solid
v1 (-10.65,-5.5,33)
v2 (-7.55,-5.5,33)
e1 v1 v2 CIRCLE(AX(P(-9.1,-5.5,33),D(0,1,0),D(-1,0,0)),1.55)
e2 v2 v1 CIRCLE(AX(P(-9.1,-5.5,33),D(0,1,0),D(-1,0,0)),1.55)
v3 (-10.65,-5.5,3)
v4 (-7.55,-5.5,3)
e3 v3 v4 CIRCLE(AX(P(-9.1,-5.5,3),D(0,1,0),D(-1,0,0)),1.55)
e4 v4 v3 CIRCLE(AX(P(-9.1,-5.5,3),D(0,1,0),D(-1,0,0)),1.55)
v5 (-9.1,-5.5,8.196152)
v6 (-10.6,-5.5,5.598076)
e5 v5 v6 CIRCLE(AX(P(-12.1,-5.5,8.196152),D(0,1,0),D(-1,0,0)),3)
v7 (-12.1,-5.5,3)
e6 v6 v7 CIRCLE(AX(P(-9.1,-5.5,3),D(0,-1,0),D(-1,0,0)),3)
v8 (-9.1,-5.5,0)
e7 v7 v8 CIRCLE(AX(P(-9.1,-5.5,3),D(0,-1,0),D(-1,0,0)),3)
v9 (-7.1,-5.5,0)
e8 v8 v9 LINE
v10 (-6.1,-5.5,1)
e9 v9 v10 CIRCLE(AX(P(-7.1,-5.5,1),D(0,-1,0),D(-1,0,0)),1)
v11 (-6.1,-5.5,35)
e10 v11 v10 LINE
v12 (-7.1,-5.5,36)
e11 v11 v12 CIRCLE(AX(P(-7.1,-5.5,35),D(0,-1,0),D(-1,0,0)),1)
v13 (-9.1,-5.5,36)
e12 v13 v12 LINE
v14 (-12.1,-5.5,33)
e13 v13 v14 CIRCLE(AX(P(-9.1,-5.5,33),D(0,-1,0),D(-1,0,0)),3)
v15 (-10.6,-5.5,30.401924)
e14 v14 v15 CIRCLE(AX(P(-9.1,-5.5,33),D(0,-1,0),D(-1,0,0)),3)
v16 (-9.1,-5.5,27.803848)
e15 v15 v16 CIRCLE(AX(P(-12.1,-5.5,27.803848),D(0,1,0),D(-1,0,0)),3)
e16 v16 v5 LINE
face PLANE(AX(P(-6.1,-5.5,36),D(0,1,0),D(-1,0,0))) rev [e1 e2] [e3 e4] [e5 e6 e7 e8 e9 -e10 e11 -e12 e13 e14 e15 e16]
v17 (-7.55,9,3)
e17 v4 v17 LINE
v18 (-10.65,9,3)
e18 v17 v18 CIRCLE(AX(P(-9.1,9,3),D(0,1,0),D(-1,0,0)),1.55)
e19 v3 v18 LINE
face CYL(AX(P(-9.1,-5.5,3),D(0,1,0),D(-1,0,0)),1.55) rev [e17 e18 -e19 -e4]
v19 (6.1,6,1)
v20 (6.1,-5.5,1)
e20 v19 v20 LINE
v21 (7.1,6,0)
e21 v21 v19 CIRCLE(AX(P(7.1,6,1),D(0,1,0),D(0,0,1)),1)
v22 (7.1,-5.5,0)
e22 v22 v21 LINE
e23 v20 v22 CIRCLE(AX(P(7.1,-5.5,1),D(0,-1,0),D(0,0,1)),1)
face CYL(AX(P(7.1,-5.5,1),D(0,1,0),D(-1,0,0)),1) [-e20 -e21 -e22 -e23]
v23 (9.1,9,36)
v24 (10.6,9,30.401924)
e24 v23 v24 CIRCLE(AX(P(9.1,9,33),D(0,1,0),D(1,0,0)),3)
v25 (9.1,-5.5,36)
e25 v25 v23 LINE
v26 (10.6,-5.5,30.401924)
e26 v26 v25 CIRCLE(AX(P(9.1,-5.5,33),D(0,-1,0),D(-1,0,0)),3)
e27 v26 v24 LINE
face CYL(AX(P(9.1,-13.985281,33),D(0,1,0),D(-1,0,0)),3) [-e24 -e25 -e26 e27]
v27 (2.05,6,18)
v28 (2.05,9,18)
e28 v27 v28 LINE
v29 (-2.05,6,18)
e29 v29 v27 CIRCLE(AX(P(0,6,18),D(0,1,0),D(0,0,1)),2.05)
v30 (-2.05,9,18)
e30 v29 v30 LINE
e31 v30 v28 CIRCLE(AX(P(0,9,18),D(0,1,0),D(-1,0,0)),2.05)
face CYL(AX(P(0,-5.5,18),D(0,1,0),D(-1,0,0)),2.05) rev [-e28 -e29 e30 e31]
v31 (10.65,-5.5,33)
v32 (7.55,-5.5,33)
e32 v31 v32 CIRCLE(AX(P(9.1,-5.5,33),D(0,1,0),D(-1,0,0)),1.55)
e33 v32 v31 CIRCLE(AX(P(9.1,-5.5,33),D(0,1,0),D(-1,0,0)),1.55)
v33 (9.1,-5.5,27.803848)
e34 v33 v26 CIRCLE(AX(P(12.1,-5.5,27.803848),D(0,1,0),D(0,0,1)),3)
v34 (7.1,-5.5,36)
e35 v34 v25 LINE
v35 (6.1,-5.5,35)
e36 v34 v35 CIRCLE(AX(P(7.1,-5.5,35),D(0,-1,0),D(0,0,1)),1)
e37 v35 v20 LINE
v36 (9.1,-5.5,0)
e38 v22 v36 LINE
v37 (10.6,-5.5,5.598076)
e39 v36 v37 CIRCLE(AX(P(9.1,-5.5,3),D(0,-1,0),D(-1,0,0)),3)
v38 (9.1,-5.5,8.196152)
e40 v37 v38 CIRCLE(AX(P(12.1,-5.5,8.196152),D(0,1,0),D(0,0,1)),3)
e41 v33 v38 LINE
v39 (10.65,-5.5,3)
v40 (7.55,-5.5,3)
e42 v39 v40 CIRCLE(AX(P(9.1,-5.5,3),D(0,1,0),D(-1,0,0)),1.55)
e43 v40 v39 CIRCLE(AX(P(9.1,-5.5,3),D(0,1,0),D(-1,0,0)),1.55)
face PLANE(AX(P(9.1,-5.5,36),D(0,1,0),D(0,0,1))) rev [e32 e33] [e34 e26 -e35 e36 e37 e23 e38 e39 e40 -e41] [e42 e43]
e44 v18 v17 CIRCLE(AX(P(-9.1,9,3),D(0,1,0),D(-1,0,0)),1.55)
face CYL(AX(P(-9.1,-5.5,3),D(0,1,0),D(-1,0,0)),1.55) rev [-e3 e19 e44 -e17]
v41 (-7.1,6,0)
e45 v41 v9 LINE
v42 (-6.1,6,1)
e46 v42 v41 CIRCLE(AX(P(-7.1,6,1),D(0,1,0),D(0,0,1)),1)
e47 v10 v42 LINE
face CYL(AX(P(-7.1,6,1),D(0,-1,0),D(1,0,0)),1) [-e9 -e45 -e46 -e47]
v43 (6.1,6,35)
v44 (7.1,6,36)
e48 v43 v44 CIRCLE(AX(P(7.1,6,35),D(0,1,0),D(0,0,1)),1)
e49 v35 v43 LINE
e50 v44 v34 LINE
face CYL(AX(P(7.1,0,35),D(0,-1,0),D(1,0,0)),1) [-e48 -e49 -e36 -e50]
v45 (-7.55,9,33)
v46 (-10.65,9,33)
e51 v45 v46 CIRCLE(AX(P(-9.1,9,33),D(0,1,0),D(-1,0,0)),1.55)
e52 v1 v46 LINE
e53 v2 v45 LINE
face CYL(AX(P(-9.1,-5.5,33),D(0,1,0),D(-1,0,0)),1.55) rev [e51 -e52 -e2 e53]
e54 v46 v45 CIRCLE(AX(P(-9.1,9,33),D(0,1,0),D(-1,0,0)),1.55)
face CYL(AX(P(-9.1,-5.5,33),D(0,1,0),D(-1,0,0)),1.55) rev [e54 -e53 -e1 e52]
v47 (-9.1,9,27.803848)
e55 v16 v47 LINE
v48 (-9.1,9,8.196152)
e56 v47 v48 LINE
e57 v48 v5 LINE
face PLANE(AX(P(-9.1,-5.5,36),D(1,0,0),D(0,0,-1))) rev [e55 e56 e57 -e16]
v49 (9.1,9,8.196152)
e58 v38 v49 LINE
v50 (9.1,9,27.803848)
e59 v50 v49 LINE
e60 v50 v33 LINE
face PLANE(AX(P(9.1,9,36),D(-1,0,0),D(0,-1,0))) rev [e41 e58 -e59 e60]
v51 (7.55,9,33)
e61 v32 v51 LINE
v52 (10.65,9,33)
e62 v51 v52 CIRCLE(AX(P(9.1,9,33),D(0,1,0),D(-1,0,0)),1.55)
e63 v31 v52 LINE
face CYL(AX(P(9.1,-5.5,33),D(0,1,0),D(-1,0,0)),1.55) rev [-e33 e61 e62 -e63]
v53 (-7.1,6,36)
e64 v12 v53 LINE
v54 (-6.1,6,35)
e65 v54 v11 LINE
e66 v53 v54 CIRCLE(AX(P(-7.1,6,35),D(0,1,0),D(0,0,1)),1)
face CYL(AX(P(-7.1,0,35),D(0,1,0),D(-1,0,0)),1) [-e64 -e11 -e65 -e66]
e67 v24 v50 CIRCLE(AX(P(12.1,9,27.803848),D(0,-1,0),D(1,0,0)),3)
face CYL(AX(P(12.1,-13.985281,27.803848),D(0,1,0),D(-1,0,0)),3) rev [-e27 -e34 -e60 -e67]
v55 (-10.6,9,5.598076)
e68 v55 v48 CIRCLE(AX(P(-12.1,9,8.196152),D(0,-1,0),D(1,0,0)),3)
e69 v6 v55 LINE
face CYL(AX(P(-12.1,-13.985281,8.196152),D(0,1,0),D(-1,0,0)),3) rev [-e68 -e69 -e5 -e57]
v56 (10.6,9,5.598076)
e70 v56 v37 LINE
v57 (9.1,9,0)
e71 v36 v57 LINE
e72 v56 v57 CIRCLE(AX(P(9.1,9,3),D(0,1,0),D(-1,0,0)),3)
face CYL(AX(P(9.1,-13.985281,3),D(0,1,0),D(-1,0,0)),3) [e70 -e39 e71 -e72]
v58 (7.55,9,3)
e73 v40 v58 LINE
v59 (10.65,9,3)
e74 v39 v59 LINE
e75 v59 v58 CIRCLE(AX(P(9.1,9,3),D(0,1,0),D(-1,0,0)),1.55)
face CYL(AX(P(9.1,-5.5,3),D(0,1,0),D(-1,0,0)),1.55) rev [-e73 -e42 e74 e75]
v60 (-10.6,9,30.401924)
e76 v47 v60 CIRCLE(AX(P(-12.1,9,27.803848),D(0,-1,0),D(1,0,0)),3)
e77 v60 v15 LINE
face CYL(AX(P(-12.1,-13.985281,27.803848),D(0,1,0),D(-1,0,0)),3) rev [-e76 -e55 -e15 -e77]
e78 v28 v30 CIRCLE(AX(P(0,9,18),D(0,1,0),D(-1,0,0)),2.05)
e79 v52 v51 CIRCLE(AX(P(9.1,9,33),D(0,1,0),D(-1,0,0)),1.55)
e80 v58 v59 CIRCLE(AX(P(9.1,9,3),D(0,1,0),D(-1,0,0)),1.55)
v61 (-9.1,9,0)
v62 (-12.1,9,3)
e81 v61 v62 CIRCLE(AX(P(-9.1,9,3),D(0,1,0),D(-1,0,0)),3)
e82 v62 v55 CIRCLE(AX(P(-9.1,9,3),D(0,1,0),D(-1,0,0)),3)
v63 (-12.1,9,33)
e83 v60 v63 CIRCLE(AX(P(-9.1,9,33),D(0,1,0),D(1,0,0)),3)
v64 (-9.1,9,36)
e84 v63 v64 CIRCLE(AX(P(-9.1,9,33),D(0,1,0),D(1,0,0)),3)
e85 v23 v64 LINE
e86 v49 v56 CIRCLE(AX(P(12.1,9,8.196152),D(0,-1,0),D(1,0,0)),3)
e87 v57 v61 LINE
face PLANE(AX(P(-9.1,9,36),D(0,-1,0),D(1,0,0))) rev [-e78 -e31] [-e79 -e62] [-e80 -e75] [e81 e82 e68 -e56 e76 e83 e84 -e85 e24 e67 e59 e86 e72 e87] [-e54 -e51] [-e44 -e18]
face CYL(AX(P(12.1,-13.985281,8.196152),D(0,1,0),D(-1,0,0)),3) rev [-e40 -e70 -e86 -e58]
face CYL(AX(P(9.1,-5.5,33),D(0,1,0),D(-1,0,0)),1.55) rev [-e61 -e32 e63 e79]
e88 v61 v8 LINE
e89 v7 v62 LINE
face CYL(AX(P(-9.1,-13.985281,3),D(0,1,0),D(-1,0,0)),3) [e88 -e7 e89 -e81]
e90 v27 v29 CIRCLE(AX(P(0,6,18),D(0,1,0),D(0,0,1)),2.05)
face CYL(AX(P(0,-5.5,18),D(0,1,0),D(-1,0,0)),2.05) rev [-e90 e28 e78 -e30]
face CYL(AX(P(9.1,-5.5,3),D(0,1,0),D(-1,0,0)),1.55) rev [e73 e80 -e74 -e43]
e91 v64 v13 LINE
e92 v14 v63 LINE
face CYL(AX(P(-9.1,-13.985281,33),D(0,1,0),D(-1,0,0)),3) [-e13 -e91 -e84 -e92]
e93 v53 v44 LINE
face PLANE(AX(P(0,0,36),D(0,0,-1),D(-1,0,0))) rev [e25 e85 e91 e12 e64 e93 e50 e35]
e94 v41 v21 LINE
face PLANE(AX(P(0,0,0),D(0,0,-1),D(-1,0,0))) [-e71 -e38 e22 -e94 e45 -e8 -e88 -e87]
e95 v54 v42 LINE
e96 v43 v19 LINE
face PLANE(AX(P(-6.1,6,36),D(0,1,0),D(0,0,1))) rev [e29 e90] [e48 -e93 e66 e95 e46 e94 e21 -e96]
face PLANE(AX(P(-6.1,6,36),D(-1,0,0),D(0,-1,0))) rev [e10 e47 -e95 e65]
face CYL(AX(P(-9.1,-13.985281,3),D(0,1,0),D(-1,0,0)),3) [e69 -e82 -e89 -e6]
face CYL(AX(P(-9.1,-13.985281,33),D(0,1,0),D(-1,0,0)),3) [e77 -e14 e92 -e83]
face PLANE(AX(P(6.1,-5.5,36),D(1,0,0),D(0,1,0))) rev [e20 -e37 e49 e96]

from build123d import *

# Parameters (mm, degrees)
EXTRUDE_1_DEPTH     = 36
SKETCH_2_R          = 3
EXTRUDE_2_DEPTH     = 14.5
SKETCH_3_R          = 1.55
SKETCH_3_R_2        = 2.05
CUT_EXTRUDE_1_DEPTH = 41.652921174
FILLET_1_R          = 3
FILLET_2_R          = 1


with BuildPart() as part:
    # 草图1 → 凸台-拉伸1 (new body)
    with BuildSketch(Plane.XY):
        Polygon((-6.1, 6), (6.1, 6), (6.1, -5.5), (9.1, -5.5), (9.1, 9), (-9.1, 9), (-9.1, -5.5), (-6.1, -5.5), align=None)
    extrude(amount=EXTRUDE_1_DEPTH)

    # 草图2 → 凸台-拉伸2 (add)
    with BuildSketch(Plane(origin=(0, 9, 0), x_dir=(1, 0, 0), z_dir=(0, 1, 0))):
        with Locations((9.1, -3)):
            Circle(SKETCH_2_R)
        with Locations((-9.1, -3)):
            Circle(SKETCH_2_R)
        with Locations((9.1, -33)):
            Circle(SKETCH_2_R)
        with Locations((-9.1, -33)):
            Circle(SKETCH_2_R)
    extrude(amount=-EXTRUDE_2_DEPTH)

    # 草图3 → 切除-拉伸1 (cut, through all)
    with BuildSketch(Plane(origin=(0, 9, 0), x_dir=(1, 0, 0), z_dir=(0, 1, 0))):
        with Locations(Location((9.1, -3, 0), (0, 0, 180))):
            Circle(SKETCH_3_R)
        with Locations(Location((-9.1, -33, 0), (0, 0, 180))):
            Circle(SKETCH_3_R)
        with Locations(Location((9.1, -33, 0), (0, 0, 180))):
            Circle(SKETCH_3_R)
        with Locations(Location((-9.1, -3, 0), (0, 0, 180))):
            Circle(SKETCH_3_R)
        with Locations(Location((0, -18, 0), (0, 0, 180))):
            Circle(SKETCH_3_R_2)
    extrude(amount=-CUT_EXTRUDE_1_DEPTH, mode=Mode.SUBTRACT)

    # 圆角1
    fillet_1_edges = [part.edges().sort_by_distance(p)[0] for p in [
        (9.1, 1.75, 6),
        (-9.1, 1.75, 6),
        (9.1, 1.75, 30),
        (-9.1, 1.75, 30),
    ]]
    fillet(fillet_1_edges, radius=FILLET_1_R)

    # 圆角2
    fillet_2_edges = [part.edges().sort_by_distance(p)[0] for p in [
        (6.1, 0.25, 0),
        (-6.1, 0.25, 0),
        (6.1, 0.25, 36),
        (-6.1, 0.25, 36),
    ]]
    fillet(fillet_2_edges, radius=FILLET_2_R)


solid = part.part
